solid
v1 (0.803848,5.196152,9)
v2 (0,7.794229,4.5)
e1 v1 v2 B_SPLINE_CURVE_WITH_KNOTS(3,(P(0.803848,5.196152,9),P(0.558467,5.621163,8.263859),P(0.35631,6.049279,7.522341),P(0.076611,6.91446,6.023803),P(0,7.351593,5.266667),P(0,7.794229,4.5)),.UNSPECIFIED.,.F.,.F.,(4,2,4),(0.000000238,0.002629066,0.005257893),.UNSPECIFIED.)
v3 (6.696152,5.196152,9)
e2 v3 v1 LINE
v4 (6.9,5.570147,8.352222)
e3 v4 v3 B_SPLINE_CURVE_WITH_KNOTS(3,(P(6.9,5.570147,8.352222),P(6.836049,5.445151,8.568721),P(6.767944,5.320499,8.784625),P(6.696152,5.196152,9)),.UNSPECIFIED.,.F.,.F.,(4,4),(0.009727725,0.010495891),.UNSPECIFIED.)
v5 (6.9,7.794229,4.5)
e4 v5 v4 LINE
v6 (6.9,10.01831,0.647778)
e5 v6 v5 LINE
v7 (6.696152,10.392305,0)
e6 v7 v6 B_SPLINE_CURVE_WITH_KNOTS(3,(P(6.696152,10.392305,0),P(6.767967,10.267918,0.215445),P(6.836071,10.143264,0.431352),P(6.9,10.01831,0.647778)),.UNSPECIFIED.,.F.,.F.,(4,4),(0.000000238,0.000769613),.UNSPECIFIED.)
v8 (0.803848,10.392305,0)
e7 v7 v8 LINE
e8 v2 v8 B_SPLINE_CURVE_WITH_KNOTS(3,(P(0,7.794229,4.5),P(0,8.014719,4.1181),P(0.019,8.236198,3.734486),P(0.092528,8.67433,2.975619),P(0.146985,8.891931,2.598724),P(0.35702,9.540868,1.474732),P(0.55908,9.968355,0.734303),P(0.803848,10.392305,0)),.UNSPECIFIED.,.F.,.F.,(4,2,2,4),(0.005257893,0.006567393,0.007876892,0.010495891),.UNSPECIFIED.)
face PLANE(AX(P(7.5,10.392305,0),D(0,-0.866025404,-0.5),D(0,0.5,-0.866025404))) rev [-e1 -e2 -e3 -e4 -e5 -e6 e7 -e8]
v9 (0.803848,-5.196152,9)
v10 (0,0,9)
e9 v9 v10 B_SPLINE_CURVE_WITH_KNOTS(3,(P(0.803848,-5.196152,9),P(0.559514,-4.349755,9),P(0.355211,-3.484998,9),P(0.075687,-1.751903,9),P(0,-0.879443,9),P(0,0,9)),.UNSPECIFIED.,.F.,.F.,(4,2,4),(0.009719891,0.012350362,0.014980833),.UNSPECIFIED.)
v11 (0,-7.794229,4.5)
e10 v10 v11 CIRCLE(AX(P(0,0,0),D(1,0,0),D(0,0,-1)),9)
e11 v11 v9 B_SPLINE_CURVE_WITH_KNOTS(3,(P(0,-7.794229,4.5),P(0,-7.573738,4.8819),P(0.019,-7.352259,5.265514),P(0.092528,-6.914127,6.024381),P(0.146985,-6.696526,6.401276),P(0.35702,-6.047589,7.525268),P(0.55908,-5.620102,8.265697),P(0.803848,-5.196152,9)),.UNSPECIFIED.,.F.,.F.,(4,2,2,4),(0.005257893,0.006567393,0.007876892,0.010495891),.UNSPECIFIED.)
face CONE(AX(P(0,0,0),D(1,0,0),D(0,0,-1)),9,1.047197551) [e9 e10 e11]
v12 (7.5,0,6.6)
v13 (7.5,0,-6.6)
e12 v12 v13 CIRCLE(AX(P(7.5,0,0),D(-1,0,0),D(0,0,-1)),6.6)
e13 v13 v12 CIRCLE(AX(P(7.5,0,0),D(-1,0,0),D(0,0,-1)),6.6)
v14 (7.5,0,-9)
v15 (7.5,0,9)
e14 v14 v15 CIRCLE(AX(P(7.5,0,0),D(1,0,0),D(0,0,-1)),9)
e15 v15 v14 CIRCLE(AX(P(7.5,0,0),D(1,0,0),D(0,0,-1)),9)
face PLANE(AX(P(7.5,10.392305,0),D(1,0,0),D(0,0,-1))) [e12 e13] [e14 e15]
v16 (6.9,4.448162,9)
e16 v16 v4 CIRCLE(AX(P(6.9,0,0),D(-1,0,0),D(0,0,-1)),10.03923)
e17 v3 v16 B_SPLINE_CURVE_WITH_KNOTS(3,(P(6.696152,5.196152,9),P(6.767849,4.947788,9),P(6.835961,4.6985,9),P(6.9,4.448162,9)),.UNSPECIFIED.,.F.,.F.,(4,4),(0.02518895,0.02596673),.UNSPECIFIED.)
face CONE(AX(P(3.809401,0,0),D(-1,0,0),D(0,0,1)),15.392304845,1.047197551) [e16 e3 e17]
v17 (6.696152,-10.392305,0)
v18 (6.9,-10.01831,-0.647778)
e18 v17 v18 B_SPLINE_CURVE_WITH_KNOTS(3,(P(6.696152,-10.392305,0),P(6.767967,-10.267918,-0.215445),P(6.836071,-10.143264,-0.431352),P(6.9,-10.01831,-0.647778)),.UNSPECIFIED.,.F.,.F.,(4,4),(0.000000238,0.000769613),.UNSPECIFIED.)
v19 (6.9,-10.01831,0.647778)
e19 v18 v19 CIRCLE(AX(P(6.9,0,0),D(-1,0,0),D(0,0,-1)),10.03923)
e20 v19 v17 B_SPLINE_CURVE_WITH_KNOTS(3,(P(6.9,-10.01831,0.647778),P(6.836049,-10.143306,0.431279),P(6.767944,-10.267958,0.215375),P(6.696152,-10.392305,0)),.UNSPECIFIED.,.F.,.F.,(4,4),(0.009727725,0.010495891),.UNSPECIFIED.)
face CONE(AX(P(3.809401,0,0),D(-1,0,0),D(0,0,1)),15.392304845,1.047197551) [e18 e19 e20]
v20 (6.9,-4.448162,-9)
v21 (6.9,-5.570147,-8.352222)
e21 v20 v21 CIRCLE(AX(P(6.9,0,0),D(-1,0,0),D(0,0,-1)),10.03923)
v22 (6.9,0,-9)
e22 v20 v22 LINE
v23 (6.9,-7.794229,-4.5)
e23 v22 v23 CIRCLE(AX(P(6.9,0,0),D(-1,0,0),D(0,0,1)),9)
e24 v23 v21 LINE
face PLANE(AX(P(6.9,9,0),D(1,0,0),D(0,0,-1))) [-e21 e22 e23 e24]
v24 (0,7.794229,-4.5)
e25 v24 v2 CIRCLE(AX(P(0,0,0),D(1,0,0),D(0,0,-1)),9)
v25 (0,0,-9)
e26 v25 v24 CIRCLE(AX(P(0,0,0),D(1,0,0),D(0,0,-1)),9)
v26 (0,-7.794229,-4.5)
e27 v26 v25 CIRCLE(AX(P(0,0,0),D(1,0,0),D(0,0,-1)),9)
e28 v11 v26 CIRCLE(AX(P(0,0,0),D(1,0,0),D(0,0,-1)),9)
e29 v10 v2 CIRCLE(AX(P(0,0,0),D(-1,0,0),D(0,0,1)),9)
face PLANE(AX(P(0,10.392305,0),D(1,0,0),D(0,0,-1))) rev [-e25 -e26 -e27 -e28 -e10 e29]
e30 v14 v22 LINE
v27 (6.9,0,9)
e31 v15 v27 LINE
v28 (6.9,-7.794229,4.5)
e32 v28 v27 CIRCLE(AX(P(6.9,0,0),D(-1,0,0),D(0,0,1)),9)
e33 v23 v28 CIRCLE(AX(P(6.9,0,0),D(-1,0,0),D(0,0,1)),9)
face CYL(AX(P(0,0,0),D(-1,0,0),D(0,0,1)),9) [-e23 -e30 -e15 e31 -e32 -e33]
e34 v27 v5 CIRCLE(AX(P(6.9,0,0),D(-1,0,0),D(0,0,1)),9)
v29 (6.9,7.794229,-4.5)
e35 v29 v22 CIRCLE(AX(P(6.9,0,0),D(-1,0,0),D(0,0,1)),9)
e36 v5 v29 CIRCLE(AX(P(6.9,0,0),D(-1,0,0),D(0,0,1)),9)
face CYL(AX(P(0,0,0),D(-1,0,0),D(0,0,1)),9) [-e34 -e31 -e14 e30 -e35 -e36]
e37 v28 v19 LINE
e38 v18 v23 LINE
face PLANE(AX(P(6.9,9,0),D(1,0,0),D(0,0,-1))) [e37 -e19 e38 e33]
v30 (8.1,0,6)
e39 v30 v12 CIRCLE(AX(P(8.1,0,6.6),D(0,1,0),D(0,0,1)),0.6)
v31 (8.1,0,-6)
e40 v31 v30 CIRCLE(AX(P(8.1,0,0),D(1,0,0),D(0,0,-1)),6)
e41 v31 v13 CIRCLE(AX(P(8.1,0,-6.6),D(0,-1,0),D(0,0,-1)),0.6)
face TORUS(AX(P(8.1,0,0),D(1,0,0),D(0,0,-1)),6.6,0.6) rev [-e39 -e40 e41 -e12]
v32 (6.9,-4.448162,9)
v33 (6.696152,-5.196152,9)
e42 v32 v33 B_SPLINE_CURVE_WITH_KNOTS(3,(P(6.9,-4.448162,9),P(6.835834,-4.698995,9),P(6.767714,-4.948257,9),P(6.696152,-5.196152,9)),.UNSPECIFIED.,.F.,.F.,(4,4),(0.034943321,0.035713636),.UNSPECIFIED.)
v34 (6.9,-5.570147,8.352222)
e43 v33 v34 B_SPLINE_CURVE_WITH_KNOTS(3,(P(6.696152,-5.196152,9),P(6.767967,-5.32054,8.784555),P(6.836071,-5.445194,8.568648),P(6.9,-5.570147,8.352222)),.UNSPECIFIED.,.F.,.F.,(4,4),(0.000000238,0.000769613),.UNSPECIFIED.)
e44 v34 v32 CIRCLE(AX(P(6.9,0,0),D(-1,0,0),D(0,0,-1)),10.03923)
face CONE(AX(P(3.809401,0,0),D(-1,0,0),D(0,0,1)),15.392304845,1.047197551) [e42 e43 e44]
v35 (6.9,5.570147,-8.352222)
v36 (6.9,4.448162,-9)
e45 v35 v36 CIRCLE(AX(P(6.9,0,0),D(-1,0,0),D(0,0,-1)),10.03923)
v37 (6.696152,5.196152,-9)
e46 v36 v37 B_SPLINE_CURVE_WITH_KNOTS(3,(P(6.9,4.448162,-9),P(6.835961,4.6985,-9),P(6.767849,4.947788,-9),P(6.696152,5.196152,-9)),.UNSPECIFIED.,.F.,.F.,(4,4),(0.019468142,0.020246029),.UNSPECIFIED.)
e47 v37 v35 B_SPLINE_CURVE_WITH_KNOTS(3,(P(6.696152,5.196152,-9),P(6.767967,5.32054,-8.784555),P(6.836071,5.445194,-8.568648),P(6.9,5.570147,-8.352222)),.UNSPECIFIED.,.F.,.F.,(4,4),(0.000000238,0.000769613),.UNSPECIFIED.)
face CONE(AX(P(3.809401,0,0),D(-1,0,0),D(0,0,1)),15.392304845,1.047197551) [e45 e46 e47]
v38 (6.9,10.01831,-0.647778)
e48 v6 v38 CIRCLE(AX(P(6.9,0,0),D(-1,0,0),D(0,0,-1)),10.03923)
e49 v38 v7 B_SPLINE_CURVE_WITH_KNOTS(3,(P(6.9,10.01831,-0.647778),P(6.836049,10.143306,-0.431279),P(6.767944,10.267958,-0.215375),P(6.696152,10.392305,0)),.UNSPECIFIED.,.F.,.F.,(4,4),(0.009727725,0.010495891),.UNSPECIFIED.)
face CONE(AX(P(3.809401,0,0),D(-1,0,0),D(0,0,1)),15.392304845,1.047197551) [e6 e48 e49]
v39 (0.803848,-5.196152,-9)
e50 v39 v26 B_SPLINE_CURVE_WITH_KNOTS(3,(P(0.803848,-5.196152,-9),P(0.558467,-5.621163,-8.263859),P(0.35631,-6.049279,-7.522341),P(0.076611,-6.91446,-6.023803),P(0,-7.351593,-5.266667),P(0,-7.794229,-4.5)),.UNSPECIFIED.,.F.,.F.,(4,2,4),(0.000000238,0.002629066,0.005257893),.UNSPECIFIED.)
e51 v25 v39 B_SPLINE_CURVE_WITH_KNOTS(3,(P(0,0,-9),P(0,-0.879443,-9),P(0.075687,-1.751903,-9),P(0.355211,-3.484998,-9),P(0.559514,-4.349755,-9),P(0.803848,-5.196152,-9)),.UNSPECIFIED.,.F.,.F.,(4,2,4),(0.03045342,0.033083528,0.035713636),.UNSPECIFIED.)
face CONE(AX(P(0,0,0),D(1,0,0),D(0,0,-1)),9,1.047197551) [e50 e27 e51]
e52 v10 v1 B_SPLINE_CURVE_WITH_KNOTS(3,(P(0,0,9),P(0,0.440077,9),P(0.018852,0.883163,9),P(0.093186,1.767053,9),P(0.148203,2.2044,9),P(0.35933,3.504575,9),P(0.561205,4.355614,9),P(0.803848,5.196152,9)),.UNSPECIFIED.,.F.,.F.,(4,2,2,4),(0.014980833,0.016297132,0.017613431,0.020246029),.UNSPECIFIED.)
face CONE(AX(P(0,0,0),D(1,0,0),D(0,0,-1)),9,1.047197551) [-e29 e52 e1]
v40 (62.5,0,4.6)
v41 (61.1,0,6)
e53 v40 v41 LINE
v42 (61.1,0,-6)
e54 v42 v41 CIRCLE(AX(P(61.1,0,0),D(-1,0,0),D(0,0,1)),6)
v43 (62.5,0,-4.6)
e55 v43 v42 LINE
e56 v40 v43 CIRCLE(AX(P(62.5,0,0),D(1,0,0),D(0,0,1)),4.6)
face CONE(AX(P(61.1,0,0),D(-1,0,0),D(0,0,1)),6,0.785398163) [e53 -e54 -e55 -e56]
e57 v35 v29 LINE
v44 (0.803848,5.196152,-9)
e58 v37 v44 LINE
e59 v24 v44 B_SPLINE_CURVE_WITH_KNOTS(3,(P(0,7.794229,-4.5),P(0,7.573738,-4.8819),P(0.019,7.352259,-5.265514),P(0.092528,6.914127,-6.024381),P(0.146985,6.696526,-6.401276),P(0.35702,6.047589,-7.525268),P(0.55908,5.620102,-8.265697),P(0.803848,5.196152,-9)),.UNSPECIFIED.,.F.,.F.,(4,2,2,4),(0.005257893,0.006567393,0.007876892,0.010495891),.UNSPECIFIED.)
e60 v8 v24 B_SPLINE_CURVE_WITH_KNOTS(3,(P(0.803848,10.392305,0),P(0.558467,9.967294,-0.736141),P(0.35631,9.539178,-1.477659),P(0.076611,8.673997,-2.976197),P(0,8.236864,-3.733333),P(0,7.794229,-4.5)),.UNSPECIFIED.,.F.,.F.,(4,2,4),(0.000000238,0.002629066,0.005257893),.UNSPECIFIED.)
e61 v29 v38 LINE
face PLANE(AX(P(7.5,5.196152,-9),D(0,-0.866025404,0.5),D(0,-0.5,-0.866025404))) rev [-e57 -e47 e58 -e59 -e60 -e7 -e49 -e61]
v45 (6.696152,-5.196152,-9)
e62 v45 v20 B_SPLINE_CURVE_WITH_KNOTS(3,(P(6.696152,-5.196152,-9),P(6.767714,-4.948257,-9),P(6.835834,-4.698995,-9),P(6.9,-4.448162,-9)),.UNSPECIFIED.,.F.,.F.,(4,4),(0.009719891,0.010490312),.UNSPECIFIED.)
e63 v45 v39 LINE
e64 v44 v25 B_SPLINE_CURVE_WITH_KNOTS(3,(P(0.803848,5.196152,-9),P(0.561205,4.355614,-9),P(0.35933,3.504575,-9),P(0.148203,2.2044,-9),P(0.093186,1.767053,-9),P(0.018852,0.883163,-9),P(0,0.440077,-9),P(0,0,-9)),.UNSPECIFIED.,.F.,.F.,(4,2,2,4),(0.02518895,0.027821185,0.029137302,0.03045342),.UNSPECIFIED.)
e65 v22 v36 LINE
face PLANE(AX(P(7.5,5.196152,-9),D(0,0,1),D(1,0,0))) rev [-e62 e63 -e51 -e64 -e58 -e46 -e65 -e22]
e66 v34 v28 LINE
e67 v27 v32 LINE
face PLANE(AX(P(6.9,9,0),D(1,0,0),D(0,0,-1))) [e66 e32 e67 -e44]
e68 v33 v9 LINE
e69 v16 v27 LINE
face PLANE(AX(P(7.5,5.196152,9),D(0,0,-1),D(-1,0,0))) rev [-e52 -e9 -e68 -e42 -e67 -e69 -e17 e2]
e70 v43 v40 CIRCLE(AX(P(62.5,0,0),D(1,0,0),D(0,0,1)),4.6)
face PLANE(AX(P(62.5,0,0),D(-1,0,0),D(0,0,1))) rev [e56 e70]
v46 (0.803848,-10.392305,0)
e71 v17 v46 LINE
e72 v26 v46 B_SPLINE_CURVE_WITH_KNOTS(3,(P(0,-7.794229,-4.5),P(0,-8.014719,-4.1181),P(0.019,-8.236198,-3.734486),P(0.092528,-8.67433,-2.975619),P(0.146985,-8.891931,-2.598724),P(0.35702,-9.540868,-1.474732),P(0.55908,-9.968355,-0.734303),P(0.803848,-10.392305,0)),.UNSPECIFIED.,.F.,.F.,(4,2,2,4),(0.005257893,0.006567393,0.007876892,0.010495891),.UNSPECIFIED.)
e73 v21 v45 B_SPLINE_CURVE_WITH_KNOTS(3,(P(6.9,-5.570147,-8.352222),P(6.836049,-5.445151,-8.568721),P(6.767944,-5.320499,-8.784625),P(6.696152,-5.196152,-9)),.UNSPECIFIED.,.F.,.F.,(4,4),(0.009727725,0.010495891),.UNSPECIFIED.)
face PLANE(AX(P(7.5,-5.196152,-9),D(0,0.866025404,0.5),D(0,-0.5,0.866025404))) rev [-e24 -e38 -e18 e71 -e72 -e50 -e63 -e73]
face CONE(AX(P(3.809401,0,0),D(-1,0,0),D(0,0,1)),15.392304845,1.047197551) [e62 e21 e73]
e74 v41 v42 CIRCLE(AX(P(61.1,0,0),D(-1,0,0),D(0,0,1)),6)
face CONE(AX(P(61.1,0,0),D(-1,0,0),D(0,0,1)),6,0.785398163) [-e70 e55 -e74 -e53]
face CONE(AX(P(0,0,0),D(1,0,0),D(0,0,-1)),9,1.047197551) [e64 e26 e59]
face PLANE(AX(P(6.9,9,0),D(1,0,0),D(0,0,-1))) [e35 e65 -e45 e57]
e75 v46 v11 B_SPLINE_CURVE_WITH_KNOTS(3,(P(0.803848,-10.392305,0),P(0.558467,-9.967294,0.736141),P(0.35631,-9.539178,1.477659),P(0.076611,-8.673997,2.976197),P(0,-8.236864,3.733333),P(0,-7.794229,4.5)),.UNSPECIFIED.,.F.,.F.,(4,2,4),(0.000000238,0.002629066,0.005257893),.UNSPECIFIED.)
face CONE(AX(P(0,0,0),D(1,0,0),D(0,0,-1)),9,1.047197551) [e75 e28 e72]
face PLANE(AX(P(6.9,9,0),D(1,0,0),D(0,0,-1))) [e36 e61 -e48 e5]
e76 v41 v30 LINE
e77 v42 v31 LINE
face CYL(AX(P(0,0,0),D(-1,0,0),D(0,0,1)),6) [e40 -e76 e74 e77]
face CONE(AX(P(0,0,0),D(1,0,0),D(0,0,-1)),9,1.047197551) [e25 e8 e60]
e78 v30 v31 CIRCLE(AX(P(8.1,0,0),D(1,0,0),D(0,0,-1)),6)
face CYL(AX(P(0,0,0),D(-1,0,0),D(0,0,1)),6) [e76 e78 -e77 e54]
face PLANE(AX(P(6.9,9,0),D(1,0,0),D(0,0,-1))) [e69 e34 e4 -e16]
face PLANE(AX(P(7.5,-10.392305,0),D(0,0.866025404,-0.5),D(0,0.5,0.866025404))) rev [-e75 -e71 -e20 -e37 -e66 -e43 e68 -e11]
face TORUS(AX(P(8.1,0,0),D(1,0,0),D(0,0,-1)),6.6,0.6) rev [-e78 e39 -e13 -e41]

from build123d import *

# Parameters (mm, degrees)
BASE_EXTRUDE_DEPTH = 7.5
SKETCH4_W          = 0.6
SKETCH4_H          = 11.392304845
CHAMFER_2_SIZE     = 1.4
FILLET_2_R         = 0.6


with BuildPart() as part:
    # Sketch1 → Base-Extrude (new body)
    with BuildSketch(Plane(origin=(0, 0, 0), x_dir=(0, 0, -1), z_dir=(1, 0, 0))):
        Polygon((9, 5.196152423), (9, -5.196152423), (0, -10.392304845), (-9, -5.196152423), (-9, 5.196152423), (0, 10.392304845), align=None)
    extrude(amount=BASE_EXTRUDE_DEPTH)

    # Sketch2 → Boss-Revolve1 (revolve)
    with BuildSketch(Plane.XY, mode=Mode.PRIVATE) as boss_revolve1_sk:
        Polygon((0, 0), (62.5, 0), (62.5, 4.4845), (62.5, 6), (7.791693541, 6), (0, 6), align=None)
    revolve(boss_revolve1_sk.sketch.rotate(Axis((0, 0, 0), (1, 0, 0)), 90), axis=Axis((0, 0, 0), (1, 0, 0)))

    # Sketch3 → Cut-Revolve1 (revolve, cut)
    with BuildSketch(Plane.XY):
        Polygon((0, 9), (3.690598923, 15.392304845), (3.690598923, 20.392304845), (-10, 20.392304845), (-10, 9), align=None)
    revolve(axis=Axis((0, 0, 0), (1, 0, 0)), mode=Mode.SUBTRACT)

    # Sketch5 → Cut-Revolve2 (revolve, cut)
    with BuildSketch(Plane.XY):
        Polygon((7.5, 9), (3.809401077, 15.392304845), (3.809401077, 20.392304845), (13.809401077, 20.392304845), (13.809401077, 9), align=None)
    revolve(axis=Axis((0, 0, 0), (1, 0, 0)), mode=Mode.SUBTRACT)

    # Sketch4 → Cut-Revolve3 (revolve, cut)
    with BuildSketch(Plane.XY, mode=Mode.PRIVATE) as cut_revolve3_sk:
        with Locations((7.2, 14.696152423)):
            Rectangle(SKETCH4_W, SKETCH4_H)
    revolve(cut_revolve3_sk.sketch.rotate(Axis((0, 0, 0), (1, 0, 0)), 270), axis=Axis((0, 0, 0), (1, 0, 0)), mode=Mode.SUBTRACT)

    # Chamfer 2
    chamfer_2_edges = [part.edges().sort_by_distance(p)[0] for p in [
        (62.5, 0, -6),
    ]]
    chamfer(chamfer_2_edges, length=CHAMFER_2_SIZE)

    # Fillet 2
    fillet_2_edges = [part.edges().sort_by_distance(p)[0] for p in [
        (7.5, 0, -6),
    ]]
    fillet(fillet_2_edges, radius=FILLET_2_R)


solid = part.part
